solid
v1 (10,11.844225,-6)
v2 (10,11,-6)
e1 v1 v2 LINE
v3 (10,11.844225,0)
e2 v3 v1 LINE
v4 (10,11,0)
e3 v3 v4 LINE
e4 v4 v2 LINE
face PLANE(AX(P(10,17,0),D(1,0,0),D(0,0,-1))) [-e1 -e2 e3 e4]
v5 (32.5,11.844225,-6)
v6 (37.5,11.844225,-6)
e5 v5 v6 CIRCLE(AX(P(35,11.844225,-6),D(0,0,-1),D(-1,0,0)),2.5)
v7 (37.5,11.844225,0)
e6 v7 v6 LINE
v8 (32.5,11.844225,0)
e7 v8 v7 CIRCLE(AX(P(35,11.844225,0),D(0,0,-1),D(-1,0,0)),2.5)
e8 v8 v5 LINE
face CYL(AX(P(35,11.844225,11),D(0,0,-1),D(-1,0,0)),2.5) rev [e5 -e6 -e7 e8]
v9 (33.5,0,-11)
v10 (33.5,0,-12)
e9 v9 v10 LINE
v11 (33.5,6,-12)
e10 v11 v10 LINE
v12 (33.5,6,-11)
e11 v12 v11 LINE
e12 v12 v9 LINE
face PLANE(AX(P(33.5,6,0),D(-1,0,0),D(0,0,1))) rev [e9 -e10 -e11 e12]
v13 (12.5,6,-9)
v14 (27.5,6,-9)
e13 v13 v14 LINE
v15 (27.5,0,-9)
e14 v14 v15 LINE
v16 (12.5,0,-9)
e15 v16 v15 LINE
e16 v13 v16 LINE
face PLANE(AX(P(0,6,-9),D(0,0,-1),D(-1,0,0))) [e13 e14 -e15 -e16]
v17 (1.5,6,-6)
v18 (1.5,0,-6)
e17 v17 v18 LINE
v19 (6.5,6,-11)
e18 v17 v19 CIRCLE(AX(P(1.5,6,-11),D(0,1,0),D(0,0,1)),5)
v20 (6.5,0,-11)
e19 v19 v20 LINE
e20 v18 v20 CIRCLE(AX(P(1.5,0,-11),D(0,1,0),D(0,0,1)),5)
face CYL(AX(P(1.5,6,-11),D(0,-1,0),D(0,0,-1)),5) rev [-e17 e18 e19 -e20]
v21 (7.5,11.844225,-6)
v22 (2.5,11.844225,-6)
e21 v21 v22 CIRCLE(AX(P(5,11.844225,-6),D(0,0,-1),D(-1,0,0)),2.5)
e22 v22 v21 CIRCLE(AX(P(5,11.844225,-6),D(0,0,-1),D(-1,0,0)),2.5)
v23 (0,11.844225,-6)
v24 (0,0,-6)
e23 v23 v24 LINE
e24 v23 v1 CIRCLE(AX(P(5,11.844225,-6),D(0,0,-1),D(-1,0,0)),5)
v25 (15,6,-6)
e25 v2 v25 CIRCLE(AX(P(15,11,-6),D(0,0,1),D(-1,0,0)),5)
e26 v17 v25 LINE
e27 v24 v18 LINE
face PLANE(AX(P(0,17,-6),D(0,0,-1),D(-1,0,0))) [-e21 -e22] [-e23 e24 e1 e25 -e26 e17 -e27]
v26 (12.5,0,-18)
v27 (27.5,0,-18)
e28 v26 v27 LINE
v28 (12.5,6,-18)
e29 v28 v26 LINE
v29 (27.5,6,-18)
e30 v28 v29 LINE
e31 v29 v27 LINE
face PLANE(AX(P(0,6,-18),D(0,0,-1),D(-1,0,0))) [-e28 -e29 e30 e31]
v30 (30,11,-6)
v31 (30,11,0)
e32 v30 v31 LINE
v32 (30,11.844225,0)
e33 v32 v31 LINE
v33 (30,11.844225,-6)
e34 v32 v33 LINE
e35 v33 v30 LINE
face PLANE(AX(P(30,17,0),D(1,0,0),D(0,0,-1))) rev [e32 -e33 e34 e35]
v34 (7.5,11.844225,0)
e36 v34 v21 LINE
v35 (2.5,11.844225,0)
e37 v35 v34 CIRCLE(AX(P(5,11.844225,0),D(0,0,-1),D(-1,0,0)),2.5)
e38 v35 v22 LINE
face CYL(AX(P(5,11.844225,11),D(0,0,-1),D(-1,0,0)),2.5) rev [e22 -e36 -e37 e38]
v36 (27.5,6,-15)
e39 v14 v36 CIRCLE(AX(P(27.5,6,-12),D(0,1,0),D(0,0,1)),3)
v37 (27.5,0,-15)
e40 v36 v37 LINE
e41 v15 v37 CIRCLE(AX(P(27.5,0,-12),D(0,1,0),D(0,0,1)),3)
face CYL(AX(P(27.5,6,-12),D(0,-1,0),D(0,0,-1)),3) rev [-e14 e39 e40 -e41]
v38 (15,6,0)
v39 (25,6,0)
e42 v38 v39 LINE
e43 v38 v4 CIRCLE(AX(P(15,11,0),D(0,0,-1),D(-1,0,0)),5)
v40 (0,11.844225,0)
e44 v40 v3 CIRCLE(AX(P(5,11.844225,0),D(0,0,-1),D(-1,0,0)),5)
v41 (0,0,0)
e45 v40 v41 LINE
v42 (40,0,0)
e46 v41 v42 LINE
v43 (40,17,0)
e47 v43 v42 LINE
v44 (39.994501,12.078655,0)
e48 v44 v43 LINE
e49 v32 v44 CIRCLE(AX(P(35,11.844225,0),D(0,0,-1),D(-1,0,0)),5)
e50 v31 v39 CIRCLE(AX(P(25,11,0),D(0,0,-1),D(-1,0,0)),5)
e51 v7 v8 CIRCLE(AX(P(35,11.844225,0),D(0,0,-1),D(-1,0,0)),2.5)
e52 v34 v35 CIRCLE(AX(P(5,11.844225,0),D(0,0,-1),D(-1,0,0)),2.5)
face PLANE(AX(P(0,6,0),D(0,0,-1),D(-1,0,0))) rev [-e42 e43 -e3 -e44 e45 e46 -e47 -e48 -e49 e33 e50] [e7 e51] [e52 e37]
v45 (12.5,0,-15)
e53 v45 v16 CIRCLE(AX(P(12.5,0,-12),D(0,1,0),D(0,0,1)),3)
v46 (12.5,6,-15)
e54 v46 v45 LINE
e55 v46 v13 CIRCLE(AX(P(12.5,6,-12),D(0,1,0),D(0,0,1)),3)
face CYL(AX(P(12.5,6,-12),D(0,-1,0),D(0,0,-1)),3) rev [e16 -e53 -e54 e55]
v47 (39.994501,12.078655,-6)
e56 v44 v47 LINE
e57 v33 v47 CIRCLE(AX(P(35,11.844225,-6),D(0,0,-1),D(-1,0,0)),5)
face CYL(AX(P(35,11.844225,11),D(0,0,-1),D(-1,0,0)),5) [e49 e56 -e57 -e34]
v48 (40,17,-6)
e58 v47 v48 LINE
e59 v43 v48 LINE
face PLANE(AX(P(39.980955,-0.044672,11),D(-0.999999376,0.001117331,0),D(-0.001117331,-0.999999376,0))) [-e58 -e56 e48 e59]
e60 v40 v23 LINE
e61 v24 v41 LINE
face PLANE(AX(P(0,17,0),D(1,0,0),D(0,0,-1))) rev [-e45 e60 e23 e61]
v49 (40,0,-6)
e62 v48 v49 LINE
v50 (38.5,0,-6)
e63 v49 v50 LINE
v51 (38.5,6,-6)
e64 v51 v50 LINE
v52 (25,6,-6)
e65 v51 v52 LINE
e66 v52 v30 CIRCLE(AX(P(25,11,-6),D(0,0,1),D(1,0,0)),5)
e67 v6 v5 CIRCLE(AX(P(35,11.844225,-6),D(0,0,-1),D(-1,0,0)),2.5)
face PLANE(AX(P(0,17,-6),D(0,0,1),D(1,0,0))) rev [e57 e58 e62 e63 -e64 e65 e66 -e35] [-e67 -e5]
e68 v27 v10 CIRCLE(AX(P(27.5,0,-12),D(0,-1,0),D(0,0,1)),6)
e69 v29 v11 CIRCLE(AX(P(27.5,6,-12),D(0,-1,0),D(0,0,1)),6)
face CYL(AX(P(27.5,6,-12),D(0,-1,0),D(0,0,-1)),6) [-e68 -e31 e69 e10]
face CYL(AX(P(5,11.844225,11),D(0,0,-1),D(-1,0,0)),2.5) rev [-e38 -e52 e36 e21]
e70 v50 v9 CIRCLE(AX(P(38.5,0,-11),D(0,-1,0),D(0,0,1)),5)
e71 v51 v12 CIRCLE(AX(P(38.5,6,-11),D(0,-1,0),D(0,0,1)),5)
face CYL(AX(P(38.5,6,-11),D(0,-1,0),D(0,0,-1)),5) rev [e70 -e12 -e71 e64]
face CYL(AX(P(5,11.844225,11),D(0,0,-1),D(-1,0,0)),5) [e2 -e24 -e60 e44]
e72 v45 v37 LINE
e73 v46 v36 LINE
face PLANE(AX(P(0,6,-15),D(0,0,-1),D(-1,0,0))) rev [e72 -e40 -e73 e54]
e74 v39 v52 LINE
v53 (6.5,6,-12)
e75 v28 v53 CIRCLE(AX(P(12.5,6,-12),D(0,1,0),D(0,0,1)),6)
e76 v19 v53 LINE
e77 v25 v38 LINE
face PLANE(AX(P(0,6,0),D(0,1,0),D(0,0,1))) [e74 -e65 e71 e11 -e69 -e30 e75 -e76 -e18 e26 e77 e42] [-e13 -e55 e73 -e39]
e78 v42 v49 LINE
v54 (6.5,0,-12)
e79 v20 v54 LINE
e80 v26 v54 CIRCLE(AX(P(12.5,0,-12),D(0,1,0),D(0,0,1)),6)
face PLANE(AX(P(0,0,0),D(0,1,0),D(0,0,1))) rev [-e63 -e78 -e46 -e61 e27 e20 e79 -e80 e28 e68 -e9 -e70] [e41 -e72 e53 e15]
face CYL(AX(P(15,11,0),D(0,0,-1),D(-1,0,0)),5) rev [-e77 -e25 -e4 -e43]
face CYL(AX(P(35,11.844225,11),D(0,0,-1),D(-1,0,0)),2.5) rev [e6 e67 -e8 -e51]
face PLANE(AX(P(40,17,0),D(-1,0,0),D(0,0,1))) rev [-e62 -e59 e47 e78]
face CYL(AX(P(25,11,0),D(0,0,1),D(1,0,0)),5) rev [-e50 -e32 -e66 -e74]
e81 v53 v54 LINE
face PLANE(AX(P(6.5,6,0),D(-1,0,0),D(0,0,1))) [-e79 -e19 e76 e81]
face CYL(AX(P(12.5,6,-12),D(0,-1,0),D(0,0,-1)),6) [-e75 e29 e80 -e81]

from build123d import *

# Parameters (mm, degrees)
BASE_PLATE_6MM_DEPTH      = 6
GUIDE_UPRIGHTS_17MM_DEPTH = 17
UPRIGHT_FILLETS_R5_R      = 5
UPRIGHT_CUT_A_DEPTH       = 17
UPRIGHT_CUT_B_DEPTH       = 17
UPRIGHT_CUT_C_DEPTH       = 17


with BuildPart() as part:
    # Bracket Profile Sketch → Base Plate 6mm (new body)
    with BuildSketch(Plane(origin=(0, 0, 0), x_dir=(1, 0, 0), z_dir=(0, 1, 0))):
        with BuildLine():
            Line((10, 6), (10, 0))
            Line((10, 0), (30, 0))
            Line((30, 0), (30, 6))
            Line((30, 6), (38.5, 6))
            ThreePointArc((38.5, 6), (34.964466094, 7.464466094), (33.5, 11))
            Line((33.5, 11), (33.5, 12))
            ThreePointArc((33.5, 12), (31.742640687, 16.242640687), (27.5, 18))
            Line((27.5, 18), (12.5, 18))
            ThreePointArc((12.5, 18), (8.257359313, 16.242640687), (6.5, 12))
            Line((6.5, 12), (6.5, 11))
            ThreePointArc((6.5, 11), (5.035533906, 7.464466094), (1.5, 6))
            Line((1.5, 6), (10, 6))
        make_face()
        with BuildLine():
            ThreePointArc((12.5, 9), (9.5, 12), (12.5, 15))
            Line((12.5, 15), (27.5, 15))
            ThreePointArc((27.5, 15), (30.5, 12), (27.5, 9))
            Line((27.5, 9), (12.5, 9))
        make_face(mode=Mode.SUBTRACT)
    extrude(amount=BASE_PLATE_6MM_DEPTH)

    # Sketch1_3 → Guide Uprights 17mm (add)
    with BuildSketch(Plane(origin=(0, 0, 0), x_dir=(1, 0, 0), z_dir=(0, 1, 0))):
        Polygon((30, 6), (30, 0), (40, 0), (40, 6), (38.5, 6), align=None)
        Polygon((0, 6), (0, 0), (10, 0), (10, 6), (1.5, 6), align=None)
    extrude(amount=GUIDE_UPRIGHTS_17MM_DEPTH)

    # Upright Fillets R5
    upright_fillets_r5_edges = [part.edges().sort_by_distance(p)[0] for p in [
        (10, 6, -3),
        (30, 6, -3),
    ]]
    fillet(upright_fillets_r5_edges, radius=UPRIGHT_FILLETS_R5_R)

    # Upright Cut Profiles Sketch → Upright Cut A (cut)
    with BuildSketch(Plane(origin=(0, 0, -6), x_dir=(-1, 0, 0), z_dir=(0, 0, -1))):
        with BuildLine():
            Line((-32.5, 11.844225053), (-35, 11.844225053))
            Line((-35, 11.844225053), (-37.497250612, 11.961440165))
            ThreePointArc((-37.497250612, 11.961440165), (-35.058623676, 9.344912495), (-32.5, 11.844225053))
        make_face()
        with BuildLine():
            Line((-37.497250612, 11.961440165), (-35, 11.844225053))
            Line((-35, 11.844225053), (-32.5, 11.844225053))
            ThreePointArc((-32.5, 11.844225053), (-34.941376324, 14.343537612), (-37.497250612, 11.961440165))
        make_face()
        with BuildLine():
            Line((-32.5, 11.844225053), (-35, 11.844225053))
            Line((-35, 11.844225053), (-37.497250612, 11.961440165))
            ThreePointArc((-37.497250612, 11.961440165), (-35.058623676, 9.344912495), (-32.5, 11.844225053))
        make_face()
        with BuildLine():
            Line((-37.497250612, 11.961440165), (-35, 11.844225053))
            Line((-35, 11.844225053), (-32.5, 11.844225053))
            ThreePointArc((-32.5, 11.844225053), (-34.941376324, 14.343537612), (-37.497250612, 11.961440165))
        make_face()
        with BuildLine():
            Line((-2.5, 11.844225053), (-5, 11.844225053))
            Line((-5, 11.844225053), (-7.5, 11.844225053))
            ThreePointArc((-7.5, 11.844225053), (-5, 9.344225053), (-2.5, 11.844225053))
        make_face()
        with BuildLine():
            Line((-7.5, 11.844225053), (-5, 11.844225053))
            Line((-5, 11.844225053), (-2.5, 11.844225053))
            ThreePointArc((-2.5, 11.844225053), (-5, 14.344225053), (-7.5, 11.844225053))
        make_face()
        with BuildLine():
            Line((-2.5, 11.844225053), (-5, 11.844225053))
            Line((-5, 11.844225053), (-7.5, 11.844225053))
            ThreePointArc((-7.5, 11.844225053), (-5, 9.344225053), (-2.5, 11.844225053))
        make_face()
        with BuildLine():
            Line((-7.5, 11.844225053), (-5, 11.844225053))
            Line((-5, 11.844225053), (-2.5, 11.844225053))
            ThreePointArc((-2.5, 11.844225053), (-5, 14.344225053), (-7.5, 11.844225053))
        make_face()
    extrude(amount=-UPRIGHT_CUT_A_DEPTH, mode=Mode.SUBTRACT)

    # Sketch2_7 → Upright Cut B (cut)
    with BuildSketch(Plane(origin=(0, 0, -6), x_dir=(-1, 0, 0), z_dir=(0, 0, -1))):
        with BuildLine():
            ThreePointArc((0, 11.844225053), (-5, 16.844225053), (-10, 11.844225053))
            Line((-10, 11.844225053), (-10, 17))
            Line((-10, 17), (0, 17))
            Line((0, 17), (0, 11.844225053))
        make_face()
    extrude(amount=-UPRIGHT_CUT_B_DEPTH, mode=Mode.SUBTRACT)

    # Sketch2_12 → Upright Cut C (cut)
    with BuildSketch(Plane(origin=(0, 0, -6), x_dir=(-1, 0, 0), z_dir=(0, 0, -1))):
        with BuildLine():
            Line((-40, 17), (-39.994501223, 12.078655276))
            ThreePointArc((-39.994501223, 12.078655276), (-34.882752648, 16.84285017), (-30, 11.844225053))
            Line((-30, 11.844225053), (-30, 17))
            Line((-30, 17), (-40, 17))
        make_face()
    extrude(amount=-UPRIGHT_CUT_C_DEPTH, mode=Mode.SUBTRACT)


solid = part.part
